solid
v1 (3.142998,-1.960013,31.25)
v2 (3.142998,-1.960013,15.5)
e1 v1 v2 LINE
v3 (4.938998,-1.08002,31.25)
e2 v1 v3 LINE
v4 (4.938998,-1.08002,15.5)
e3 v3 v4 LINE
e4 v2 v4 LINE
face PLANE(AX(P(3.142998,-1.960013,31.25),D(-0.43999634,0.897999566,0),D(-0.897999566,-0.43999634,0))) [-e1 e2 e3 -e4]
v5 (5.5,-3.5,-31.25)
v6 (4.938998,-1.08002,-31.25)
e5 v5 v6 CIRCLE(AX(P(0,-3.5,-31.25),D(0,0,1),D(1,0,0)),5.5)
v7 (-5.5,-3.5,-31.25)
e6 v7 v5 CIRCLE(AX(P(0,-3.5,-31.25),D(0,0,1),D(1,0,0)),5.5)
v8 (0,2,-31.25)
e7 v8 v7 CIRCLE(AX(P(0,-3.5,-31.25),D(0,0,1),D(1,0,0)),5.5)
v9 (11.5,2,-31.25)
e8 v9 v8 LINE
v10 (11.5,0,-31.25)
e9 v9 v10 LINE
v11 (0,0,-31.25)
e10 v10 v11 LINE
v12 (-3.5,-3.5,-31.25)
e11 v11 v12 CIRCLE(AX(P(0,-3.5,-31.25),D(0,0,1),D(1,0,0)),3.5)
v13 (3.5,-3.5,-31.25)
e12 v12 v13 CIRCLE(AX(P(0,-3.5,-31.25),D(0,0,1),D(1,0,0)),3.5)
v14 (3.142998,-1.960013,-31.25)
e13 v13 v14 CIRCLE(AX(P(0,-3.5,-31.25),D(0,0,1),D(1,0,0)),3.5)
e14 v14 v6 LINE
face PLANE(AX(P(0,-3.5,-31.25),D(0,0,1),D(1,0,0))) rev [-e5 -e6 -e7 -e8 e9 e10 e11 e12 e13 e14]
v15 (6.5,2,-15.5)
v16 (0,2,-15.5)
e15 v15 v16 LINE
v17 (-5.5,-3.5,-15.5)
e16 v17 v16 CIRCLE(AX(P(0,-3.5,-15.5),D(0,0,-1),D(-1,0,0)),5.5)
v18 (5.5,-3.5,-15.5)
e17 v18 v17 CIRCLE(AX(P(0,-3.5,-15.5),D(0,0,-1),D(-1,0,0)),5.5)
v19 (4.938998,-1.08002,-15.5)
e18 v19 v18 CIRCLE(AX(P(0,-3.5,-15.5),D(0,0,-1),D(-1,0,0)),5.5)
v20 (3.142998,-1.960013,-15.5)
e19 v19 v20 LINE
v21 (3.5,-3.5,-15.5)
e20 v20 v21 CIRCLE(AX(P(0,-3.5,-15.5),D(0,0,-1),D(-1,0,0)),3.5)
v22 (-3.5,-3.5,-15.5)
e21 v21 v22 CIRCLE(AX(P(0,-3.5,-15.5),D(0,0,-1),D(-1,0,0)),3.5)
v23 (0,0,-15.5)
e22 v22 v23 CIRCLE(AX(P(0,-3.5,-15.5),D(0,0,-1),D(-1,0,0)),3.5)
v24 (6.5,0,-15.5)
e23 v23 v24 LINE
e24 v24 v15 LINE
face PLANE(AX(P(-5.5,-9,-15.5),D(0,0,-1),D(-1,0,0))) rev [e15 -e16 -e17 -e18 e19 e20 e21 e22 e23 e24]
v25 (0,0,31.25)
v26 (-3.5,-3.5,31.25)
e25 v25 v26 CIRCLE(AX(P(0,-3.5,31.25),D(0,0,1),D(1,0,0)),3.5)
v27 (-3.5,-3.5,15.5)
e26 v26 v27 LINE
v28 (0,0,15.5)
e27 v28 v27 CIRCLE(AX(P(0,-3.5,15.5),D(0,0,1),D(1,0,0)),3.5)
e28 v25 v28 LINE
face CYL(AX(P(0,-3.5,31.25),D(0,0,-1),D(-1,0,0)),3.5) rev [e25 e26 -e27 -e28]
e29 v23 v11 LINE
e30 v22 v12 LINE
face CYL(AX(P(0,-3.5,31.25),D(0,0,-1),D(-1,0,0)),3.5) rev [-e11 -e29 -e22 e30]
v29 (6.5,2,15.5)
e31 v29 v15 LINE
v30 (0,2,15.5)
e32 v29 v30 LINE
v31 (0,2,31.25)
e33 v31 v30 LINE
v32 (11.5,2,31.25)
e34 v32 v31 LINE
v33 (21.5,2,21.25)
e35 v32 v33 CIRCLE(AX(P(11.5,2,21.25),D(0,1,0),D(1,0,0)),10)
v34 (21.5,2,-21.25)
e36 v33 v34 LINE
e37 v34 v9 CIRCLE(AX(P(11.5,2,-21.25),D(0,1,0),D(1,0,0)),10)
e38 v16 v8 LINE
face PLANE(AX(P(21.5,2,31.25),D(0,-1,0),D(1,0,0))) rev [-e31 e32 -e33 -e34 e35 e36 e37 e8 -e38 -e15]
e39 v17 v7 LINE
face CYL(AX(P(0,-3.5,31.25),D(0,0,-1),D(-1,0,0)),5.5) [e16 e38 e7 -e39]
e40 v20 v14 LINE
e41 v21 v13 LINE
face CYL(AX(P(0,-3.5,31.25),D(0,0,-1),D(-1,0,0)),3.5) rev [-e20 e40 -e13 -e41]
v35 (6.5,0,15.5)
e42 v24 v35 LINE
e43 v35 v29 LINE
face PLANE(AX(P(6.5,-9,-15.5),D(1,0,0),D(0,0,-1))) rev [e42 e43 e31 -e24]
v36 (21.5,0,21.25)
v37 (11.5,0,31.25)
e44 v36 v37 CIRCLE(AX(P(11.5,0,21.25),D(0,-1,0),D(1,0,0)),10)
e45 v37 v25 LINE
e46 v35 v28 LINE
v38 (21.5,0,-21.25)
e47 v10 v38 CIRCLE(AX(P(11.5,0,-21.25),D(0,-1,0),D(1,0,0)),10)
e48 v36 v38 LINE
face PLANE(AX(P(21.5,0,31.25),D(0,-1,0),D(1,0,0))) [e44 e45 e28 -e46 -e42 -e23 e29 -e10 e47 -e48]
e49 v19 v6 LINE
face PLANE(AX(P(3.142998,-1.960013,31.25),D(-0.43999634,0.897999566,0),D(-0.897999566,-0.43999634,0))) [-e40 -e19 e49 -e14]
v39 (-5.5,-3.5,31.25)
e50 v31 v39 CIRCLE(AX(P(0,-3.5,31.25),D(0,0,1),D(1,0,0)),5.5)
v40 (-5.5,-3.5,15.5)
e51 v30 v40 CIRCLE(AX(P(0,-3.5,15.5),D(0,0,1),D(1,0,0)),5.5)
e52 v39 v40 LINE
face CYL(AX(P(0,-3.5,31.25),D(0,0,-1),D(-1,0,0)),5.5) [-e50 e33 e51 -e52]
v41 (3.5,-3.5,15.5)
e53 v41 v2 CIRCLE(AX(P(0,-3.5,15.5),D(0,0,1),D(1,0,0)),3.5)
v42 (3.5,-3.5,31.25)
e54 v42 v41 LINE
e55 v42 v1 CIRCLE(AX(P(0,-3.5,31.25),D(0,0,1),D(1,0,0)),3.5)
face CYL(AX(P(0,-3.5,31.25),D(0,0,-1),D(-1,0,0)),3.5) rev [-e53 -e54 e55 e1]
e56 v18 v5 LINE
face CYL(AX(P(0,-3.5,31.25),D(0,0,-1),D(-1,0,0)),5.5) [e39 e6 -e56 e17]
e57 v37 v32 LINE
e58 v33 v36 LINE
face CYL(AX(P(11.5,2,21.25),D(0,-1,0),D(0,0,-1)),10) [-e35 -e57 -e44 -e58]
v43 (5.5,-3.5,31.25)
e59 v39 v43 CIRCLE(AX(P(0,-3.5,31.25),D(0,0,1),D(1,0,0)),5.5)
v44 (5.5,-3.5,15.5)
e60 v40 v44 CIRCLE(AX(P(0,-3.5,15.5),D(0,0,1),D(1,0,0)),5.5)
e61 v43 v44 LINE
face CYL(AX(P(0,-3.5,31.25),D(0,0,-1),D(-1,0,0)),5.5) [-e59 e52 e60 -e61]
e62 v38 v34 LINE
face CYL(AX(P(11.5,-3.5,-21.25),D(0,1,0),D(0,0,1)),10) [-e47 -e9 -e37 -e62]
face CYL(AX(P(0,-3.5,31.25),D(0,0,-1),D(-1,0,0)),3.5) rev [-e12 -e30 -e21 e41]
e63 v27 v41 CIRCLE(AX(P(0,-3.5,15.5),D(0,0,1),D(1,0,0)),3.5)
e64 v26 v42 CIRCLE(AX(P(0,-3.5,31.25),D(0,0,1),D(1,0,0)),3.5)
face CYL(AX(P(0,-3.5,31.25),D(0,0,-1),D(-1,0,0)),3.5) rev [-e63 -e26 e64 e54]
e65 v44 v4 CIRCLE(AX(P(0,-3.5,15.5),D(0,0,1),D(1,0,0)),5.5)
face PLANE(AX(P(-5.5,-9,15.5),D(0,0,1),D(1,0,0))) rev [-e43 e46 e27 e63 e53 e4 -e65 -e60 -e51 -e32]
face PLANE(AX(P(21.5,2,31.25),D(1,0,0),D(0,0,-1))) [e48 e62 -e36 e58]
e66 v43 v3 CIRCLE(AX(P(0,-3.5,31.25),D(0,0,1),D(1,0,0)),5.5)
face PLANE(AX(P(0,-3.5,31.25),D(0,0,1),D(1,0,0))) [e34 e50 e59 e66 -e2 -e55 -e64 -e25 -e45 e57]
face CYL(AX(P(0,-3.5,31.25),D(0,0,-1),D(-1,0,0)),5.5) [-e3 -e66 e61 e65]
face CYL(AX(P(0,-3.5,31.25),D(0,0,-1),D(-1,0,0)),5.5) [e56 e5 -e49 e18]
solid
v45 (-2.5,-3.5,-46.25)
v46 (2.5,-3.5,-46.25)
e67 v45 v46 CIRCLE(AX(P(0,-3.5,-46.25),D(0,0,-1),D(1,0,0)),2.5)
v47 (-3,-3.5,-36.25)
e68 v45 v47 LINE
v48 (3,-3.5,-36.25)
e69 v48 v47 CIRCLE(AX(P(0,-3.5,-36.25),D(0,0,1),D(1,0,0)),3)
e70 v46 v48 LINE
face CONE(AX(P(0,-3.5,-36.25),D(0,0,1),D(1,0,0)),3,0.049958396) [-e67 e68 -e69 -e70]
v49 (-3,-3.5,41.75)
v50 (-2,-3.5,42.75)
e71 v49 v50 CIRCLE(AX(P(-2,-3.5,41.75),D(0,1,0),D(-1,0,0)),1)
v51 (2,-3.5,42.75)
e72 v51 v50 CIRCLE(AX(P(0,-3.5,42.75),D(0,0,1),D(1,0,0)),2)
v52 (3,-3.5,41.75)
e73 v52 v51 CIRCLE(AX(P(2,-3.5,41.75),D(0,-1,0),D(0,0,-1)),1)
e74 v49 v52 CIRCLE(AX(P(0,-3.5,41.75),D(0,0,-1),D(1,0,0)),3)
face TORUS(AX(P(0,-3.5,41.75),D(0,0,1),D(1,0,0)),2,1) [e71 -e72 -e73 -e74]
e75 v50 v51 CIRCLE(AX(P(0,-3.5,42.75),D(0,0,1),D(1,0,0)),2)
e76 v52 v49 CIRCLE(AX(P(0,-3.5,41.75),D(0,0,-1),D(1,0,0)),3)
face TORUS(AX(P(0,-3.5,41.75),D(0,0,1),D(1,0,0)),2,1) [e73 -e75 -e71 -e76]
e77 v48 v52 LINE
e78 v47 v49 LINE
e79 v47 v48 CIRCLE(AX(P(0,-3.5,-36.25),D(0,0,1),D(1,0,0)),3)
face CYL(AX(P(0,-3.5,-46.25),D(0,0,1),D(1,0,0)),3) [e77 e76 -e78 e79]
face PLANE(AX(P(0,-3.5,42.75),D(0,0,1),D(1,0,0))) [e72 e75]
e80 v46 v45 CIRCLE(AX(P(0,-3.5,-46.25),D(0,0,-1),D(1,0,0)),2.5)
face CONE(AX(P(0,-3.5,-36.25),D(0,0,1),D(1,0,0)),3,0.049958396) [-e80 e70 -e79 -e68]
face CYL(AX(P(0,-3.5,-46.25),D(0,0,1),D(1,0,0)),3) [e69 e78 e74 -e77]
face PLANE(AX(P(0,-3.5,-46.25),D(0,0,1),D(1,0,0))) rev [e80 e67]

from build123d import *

# Parameters (mm, degrees)
EXTRUDE_5_DEPTH     = 31.25
SKETCH_4_W          = 12
SKETCH_4_H          = 31
CUT_EXTRUDE_1_DEPTH = 40.494461637
SKETCH_6_R          = 3
EXTRUDE_3_DEPTH     = 89
CHAMFER_1_SIZE      = 0.5
CHAMFER_1_SIZE2     = 10
FILLET_1_R          = 10
FILLET_2_R          = 1


with BuildPart() as part:
    # 草图3 → 拉伸-薄壁5 (new, symmetric)
    with BuildSketch(Plane.XY):
        with BuildLine():
            Line((21.5, 0), (0, 0))
            ThreePointArc((0, 0), (-1.852031969, -6.469844707), (3.142998481, -1.960012809))
            Line((3.142998481, -1.960012809), (4.938997613, -1.080020128))
            ThreePointArc((4.938997613, -1.080020128), (-2.910335952, -8.166898826), (0, 2))
            Line((0, 2), (21.5, 2))
            Line((21.5, 2), (21.5, 0))
        make_face()
    extrude(amount=EXTRUDE_5_DEPTH, both=True)

    # 草图4 → 切除-拉伸1 (cut, through all)
    with BuildSketch(Plane(origin=(0, 2, 0), x_dir=(1, 0, 0), z_dir=(0, 1, 0))):
        with Locations((0.5, 0)):
            Rectangle(SKETCH_4_W, SKETCH_4_H)
    extrude(amount=-CUT_EXTRUDE_1_DEPTH, mode=Mode.SUBTRACT)

    # 圆角1
    fillet_1_edges = [part.edges().sort_by_distance(p)[0] for p in [
        (21.5, 1, 31.25),
        (21.5, 1, -31.25),
    ]]
    fillet(fillet_1_edges, radius=FILLET_1_R)


with BuildPart() as body_2:
    # 草图6 → 凸台-拉伸3 (new body)
    with BuildSketch(Plane.XY.offset(42.75)):
        with Locations((0, -3.5)):
            Circle(SKETCH_6_R)
    extrude(amount=-EXTRUDE_3_DEPTH)

    # 倒角1
    chamfer_1_edges = [body_2.edges().sort_by_distance(p)[0] for p in [
        (-3, -3.5, -46.25),
    ]]
    chamfer_1_side = [body_2.faces().sort_by_distance(p)[0] for p in [
        (0, -3.5, -46.25),
    ]]
    chamfer(chamfer_1_edges, length=CHAMFER_1_SIZE, length2=CHAMFER_1_SIZE2, reference=chamfer_1_side[0])

    # 圆角2
    fillet_2_edges = [body_2.edges().sort_by_distance(p)[0] for p in [
        (-3, -3.5, 42.75),
    ]]
    fillet(fillet_2_edges, radius=FILLET_2_R)


solid = Compound([part.part, body_2.part])
